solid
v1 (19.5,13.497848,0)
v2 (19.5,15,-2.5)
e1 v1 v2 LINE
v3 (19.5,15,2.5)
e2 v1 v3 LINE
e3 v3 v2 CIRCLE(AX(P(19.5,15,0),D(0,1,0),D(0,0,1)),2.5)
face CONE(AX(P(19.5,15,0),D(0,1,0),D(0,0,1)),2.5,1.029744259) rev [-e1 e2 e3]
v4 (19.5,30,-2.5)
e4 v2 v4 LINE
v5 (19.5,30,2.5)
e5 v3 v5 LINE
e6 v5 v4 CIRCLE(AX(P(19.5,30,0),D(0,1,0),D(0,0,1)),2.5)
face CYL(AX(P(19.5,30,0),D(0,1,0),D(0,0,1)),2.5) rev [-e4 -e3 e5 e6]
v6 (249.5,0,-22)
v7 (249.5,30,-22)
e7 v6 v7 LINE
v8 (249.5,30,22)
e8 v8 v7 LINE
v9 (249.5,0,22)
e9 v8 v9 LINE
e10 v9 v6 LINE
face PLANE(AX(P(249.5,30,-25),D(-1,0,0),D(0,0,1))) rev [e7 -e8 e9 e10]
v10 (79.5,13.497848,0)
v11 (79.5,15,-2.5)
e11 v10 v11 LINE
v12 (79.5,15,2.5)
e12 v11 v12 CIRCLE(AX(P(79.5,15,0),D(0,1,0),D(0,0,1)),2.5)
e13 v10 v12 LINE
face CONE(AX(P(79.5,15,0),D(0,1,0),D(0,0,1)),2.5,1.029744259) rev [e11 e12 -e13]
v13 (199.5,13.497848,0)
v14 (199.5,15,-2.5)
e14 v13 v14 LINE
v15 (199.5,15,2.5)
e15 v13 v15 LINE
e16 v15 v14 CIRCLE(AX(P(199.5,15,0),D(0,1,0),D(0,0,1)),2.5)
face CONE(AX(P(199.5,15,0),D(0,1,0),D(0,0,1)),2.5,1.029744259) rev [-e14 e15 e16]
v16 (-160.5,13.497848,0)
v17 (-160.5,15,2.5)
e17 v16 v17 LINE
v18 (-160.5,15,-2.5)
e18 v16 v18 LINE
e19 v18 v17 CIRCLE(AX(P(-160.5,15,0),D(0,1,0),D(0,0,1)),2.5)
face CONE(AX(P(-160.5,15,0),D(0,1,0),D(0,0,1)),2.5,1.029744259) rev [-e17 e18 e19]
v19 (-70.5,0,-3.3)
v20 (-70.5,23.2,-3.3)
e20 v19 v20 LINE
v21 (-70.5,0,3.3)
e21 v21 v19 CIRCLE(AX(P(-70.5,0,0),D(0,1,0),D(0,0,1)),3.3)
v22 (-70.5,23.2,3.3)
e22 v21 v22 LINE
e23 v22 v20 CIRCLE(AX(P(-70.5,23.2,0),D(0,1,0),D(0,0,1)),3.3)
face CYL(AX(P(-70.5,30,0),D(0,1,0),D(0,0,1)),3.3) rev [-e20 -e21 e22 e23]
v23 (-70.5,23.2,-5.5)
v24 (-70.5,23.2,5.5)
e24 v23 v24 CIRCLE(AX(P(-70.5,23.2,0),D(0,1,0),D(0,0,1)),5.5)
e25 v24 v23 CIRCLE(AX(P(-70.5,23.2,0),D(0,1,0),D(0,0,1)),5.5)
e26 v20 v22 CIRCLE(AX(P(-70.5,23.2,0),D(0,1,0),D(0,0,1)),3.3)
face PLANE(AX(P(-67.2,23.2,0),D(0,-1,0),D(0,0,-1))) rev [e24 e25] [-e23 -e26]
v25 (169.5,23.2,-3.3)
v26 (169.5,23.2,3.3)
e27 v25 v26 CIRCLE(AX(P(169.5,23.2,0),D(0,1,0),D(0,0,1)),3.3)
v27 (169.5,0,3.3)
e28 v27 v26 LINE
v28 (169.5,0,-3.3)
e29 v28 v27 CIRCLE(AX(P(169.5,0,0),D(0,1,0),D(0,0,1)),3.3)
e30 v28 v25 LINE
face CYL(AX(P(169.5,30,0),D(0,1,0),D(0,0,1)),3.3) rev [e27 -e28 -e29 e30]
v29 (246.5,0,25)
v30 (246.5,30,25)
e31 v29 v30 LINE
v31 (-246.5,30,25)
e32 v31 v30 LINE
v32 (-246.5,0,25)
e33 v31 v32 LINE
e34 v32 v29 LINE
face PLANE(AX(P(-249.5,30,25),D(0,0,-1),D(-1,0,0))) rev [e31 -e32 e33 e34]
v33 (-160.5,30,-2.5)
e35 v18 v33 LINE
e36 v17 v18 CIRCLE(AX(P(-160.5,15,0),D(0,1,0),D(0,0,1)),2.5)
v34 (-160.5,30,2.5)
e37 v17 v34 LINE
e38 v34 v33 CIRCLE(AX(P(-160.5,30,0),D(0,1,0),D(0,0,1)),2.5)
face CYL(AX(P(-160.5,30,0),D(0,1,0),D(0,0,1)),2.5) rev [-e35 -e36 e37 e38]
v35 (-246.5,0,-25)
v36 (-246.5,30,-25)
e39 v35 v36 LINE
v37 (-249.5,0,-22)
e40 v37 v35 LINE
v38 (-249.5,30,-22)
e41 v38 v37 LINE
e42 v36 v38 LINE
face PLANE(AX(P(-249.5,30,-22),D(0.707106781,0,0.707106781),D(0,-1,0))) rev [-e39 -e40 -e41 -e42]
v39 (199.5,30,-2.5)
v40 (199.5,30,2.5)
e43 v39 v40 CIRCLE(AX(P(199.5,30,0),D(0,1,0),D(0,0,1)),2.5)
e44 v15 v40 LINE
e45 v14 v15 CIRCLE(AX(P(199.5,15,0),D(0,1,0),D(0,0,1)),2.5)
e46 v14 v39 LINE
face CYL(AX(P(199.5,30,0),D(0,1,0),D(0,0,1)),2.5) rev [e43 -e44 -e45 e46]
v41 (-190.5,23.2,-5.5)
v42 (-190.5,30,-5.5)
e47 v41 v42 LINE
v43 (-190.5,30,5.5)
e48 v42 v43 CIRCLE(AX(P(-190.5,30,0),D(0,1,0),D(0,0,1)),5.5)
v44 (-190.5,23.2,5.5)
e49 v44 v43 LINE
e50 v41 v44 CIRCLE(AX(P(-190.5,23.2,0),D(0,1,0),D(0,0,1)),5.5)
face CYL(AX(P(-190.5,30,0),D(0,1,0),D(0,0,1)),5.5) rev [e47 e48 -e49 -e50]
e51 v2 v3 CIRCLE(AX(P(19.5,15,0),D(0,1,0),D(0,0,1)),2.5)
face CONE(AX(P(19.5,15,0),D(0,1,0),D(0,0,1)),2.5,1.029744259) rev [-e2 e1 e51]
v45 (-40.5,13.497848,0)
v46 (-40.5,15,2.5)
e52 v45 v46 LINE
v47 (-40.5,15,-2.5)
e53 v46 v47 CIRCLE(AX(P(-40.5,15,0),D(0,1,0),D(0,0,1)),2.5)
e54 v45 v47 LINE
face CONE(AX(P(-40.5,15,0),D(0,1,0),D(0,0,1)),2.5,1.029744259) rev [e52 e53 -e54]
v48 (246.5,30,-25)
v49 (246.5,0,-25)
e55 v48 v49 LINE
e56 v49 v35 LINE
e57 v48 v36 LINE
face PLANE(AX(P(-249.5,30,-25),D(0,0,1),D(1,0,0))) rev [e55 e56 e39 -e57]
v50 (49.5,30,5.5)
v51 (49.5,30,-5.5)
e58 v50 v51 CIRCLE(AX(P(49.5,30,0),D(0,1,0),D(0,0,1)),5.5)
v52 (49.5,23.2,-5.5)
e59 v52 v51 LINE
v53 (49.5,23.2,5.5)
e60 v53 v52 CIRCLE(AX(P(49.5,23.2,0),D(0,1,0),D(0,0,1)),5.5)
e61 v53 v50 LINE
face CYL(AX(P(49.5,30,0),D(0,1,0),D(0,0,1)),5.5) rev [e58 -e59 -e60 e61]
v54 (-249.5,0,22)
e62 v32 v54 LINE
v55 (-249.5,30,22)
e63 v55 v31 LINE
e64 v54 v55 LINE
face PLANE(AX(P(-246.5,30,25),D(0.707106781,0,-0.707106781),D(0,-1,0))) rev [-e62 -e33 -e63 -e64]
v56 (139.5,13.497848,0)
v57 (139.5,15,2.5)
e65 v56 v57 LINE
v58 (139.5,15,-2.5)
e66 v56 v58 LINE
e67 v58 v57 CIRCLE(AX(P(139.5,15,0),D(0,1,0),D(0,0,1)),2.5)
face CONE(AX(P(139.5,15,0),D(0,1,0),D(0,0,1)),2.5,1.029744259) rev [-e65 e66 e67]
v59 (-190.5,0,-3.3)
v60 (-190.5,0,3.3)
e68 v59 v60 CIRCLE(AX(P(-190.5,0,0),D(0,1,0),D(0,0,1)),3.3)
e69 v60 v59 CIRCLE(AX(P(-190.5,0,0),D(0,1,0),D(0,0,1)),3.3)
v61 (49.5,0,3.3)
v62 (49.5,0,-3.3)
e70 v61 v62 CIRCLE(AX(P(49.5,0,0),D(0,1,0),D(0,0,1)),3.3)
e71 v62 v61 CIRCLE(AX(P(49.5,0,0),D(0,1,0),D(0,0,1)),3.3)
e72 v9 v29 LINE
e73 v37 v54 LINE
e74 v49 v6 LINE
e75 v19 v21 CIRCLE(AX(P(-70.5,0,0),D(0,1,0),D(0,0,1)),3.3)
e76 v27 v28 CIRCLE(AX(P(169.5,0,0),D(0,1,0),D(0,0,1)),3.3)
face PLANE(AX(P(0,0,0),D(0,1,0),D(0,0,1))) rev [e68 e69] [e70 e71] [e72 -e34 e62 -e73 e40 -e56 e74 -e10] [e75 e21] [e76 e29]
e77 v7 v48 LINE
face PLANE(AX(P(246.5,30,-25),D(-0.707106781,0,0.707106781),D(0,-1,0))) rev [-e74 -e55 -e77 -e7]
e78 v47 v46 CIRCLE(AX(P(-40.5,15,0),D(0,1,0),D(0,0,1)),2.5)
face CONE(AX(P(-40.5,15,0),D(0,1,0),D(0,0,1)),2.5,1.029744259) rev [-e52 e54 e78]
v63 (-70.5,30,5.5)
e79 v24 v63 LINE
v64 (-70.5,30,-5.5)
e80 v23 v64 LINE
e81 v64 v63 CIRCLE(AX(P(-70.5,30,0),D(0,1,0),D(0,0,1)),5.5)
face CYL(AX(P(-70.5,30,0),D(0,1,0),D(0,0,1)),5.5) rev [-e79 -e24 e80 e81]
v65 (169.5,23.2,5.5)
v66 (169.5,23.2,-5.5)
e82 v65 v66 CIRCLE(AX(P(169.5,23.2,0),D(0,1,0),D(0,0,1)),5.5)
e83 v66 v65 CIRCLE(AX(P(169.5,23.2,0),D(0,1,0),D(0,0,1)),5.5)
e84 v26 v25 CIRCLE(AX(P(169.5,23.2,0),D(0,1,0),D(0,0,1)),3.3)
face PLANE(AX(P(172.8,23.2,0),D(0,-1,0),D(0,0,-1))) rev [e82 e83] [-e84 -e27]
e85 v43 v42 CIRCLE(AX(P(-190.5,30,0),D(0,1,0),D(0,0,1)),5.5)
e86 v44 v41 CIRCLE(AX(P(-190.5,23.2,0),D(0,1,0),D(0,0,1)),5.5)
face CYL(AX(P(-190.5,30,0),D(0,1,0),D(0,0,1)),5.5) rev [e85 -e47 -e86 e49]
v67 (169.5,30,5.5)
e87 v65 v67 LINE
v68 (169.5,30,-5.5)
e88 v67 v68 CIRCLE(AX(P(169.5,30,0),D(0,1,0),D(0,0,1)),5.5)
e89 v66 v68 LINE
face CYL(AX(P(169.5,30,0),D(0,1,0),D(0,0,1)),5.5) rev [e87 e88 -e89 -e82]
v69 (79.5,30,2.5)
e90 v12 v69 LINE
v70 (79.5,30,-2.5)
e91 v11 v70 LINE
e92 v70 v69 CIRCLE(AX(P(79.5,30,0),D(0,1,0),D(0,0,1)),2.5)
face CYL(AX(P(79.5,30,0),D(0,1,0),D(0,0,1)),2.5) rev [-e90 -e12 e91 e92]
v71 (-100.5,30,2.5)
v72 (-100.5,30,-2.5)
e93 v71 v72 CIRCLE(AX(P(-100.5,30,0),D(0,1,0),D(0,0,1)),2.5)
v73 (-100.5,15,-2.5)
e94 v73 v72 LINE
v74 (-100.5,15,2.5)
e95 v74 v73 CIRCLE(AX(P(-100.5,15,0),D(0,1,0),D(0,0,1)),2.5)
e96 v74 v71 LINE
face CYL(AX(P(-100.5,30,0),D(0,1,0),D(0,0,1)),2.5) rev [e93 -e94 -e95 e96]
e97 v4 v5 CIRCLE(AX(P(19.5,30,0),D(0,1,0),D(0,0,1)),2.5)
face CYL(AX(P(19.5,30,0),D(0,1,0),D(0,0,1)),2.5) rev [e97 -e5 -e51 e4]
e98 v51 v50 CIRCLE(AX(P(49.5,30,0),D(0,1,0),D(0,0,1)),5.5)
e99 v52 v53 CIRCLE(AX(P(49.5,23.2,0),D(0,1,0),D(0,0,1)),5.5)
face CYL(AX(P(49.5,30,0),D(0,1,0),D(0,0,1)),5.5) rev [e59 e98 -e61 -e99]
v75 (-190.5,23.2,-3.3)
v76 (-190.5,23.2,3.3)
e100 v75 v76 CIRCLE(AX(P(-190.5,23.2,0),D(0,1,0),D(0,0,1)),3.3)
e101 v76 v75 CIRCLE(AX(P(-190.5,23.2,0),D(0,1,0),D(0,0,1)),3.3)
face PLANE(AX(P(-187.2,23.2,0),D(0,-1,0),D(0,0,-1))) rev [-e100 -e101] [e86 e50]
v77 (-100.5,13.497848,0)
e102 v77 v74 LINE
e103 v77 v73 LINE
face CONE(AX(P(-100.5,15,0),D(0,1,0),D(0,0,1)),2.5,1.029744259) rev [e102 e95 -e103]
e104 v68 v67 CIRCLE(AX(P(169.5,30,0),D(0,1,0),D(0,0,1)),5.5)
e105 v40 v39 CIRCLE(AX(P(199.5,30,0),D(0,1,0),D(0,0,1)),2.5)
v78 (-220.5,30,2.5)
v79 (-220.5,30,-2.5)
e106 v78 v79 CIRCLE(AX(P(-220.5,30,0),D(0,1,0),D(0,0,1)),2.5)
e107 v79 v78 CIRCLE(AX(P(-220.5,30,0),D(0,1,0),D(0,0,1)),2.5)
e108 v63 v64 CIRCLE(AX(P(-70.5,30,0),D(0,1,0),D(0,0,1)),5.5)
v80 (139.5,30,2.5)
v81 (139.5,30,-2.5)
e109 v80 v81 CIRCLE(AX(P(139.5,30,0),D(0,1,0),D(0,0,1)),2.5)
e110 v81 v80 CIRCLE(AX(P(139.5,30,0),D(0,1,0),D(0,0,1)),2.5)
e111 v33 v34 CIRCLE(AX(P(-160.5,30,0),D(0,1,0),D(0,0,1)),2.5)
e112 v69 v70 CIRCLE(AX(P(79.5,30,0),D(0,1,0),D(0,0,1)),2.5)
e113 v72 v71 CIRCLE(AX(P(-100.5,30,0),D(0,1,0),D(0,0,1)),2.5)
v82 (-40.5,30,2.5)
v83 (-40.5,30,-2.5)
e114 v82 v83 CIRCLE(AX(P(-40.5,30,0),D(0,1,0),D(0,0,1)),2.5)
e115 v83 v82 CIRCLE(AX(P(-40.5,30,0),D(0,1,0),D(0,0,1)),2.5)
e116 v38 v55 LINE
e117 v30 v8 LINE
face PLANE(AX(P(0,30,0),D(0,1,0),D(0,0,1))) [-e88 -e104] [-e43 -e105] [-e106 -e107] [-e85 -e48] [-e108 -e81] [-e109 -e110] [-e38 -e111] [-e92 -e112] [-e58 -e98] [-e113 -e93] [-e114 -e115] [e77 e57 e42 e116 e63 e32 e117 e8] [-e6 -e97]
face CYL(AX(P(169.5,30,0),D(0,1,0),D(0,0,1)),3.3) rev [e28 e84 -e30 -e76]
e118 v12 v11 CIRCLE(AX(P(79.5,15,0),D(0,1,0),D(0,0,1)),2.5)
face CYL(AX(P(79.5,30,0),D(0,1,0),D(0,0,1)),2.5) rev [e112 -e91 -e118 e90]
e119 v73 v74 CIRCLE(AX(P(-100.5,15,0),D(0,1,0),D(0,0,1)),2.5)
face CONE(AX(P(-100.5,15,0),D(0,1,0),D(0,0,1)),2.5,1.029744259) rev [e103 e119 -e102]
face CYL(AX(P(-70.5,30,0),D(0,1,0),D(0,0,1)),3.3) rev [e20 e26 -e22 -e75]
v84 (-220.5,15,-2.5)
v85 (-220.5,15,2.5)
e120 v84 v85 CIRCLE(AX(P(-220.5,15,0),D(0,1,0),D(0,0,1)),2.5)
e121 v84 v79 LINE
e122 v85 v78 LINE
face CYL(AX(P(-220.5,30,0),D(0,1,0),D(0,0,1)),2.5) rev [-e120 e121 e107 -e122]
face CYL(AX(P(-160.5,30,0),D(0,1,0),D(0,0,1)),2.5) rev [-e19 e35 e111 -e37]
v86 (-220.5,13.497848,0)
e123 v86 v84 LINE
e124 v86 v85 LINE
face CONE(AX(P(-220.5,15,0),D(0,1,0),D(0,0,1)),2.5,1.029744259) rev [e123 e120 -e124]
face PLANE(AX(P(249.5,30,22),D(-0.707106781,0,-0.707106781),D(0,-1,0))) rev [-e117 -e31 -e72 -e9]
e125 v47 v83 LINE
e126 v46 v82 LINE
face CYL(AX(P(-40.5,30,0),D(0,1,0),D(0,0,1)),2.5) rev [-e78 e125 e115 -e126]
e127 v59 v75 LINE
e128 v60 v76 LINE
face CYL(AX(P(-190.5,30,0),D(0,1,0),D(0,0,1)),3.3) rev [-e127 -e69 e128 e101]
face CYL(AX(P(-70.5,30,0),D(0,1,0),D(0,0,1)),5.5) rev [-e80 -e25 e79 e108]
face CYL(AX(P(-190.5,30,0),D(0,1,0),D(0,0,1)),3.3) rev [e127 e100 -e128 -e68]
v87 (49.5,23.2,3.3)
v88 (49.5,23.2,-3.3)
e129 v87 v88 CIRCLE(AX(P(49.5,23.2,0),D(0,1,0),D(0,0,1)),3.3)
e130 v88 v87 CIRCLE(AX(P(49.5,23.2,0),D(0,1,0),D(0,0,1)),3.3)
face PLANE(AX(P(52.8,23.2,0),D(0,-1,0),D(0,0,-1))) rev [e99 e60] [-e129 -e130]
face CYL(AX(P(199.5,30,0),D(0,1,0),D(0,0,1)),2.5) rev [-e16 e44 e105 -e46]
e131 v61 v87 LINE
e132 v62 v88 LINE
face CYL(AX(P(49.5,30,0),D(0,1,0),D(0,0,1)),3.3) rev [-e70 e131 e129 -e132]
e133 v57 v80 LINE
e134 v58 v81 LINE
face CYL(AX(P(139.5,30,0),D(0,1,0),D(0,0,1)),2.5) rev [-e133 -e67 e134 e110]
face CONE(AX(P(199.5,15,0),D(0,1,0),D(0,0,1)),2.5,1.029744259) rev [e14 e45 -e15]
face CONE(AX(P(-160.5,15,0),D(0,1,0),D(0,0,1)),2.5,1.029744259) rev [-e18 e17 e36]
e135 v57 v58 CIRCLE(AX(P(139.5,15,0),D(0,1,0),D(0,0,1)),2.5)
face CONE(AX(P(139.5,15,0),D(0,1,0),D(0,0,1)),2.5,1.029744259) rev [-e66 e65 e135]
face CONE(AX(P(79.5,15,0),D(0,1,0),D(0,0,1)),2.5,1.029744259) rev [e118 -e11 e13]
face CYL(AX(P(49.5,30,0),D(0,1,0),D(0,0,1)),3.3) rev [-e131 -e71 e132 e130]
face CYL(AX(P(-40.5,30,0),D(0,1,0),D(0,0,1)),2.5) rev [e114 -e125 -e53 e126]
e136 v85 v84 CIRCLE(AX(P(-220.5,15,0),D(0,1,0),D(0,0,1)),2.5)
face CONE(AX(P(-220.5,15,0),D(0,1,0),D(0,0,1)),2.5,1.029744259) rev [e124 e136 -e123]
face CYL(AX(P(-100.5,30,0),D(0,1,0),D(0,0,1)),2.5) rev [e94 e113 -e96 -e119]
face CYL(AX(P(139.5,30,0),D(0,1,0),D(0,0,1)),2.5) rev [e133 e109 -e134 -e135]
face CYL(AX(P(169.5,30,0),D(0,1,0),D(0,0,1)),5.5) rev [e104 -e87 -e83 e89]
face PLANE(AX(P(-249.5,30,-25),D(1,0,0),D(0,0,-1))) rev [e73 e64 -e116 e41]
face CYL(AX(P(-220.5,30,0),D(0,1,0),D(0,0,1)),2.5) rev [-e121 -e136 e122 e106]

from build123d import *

# Parameters (mm, degrees)
SKETCH_1_W                = 499
SKETCH_1_H                = 50
EXTRUDE_1_DEPTH           = 30
CHAMFER_1_SIZE            = 3
HOLE_WIZARD_M6_1_D        = 5
HOLE_WIZARD_M6_1_DEPTH    = 15
HOLE_WIZARD_M6_1_TIP      = 1.502151548
HOLE_WIZARD_1_D           = 6.6
HOLE_WIZARD_1_DEPTH       = 30
HOLE_WIZARD_1_CBORE_D     = 11
HOLE_WIZARD_1_CBORE_DEPTH = 6.8
HOLE_WIZARD_1_TIP         = 1.982840043


with BuildPart() as part:
    # 草图1 → 凸台-拉伸1 (new body)
    with BuildSketch(Plane(origin=(0, 0, 0), x_dir=(1, 0, 0), z_dir=(0, 1, 0))):
        Rectangle(SKETCH_1_W, SKETCH_1_H)
    extrude(amount=EXTRUDE_1_DEPTH)

    # 倒角1
    chamfer_1_edges = [part.edges().sort_by_distance(p)[0] for p in [
        (249.5, 15, 25),
        (-249.5, 15, 25),
        (-249.5, 15, -25),
        (249.5, 15, -25),
    ]]
    chamfer(chamfer_1_edges, length=CHAMFER_1_SIZE)

    # M6 螺纹孔1
    with Locations(Plane(origin=(0, 30, 0), x_dir=(1, 0, 0), z_dir=(0, 1, 0))):
        with Locations((199.5, 0), (139.5, 0), (79.5, 0), (19.5, 0), (-40.5, 0), (-100.5, 0), (-160.5, 0), (-220.5, 0)):
            Hole(HOLE_WIZARD_M6_1_D / 2, depth=HOLE_WIZARD_M6_1_DEPTH)
            with Locations((0, 0, -(HOLE_WIZARD_M6_1_DEPTH + HOLE_WIZARD_M6_1_TIP / 2))):  # 118° drill point
                Cone(0, HOLE_WIZARD_M6_1_D / 2, HOLE_WIZARD_M6_1_TIP, mode=Mode.SUBTRACT)

    # 打孔尺寸(%根据)内六角圆柱头螺钉的类型1
    with Locations(Plane(origin=(0, 30, 0), x_dir=(1, 0, 0), z_dir=(0, 1, 0))):
        with Locations((169.5, 0), (49.5, 0), (-70.5, 0), (-190.5, 0)):
            CounterBoreHole(HOLE_WIZARD_1_D / 2, HOLE_WIZARD_1_CBORE_D / 2, HOLE_WIZARD_1_CBORE_DEPTH, depth=HOLE_WIZARD_1_DEPTH)
            with Locations((0, 0, -(HOLE_WIZARD_1_DEPTH + HOLE_WIZARD_1_TIP / 2))):  # 118° drill point
                Cone(0, HOLE_WIZARD_1_D / 2, HOLE_WIZARD_1_TIP, mode=Mode.SUBTRACT)


solid = part.part
